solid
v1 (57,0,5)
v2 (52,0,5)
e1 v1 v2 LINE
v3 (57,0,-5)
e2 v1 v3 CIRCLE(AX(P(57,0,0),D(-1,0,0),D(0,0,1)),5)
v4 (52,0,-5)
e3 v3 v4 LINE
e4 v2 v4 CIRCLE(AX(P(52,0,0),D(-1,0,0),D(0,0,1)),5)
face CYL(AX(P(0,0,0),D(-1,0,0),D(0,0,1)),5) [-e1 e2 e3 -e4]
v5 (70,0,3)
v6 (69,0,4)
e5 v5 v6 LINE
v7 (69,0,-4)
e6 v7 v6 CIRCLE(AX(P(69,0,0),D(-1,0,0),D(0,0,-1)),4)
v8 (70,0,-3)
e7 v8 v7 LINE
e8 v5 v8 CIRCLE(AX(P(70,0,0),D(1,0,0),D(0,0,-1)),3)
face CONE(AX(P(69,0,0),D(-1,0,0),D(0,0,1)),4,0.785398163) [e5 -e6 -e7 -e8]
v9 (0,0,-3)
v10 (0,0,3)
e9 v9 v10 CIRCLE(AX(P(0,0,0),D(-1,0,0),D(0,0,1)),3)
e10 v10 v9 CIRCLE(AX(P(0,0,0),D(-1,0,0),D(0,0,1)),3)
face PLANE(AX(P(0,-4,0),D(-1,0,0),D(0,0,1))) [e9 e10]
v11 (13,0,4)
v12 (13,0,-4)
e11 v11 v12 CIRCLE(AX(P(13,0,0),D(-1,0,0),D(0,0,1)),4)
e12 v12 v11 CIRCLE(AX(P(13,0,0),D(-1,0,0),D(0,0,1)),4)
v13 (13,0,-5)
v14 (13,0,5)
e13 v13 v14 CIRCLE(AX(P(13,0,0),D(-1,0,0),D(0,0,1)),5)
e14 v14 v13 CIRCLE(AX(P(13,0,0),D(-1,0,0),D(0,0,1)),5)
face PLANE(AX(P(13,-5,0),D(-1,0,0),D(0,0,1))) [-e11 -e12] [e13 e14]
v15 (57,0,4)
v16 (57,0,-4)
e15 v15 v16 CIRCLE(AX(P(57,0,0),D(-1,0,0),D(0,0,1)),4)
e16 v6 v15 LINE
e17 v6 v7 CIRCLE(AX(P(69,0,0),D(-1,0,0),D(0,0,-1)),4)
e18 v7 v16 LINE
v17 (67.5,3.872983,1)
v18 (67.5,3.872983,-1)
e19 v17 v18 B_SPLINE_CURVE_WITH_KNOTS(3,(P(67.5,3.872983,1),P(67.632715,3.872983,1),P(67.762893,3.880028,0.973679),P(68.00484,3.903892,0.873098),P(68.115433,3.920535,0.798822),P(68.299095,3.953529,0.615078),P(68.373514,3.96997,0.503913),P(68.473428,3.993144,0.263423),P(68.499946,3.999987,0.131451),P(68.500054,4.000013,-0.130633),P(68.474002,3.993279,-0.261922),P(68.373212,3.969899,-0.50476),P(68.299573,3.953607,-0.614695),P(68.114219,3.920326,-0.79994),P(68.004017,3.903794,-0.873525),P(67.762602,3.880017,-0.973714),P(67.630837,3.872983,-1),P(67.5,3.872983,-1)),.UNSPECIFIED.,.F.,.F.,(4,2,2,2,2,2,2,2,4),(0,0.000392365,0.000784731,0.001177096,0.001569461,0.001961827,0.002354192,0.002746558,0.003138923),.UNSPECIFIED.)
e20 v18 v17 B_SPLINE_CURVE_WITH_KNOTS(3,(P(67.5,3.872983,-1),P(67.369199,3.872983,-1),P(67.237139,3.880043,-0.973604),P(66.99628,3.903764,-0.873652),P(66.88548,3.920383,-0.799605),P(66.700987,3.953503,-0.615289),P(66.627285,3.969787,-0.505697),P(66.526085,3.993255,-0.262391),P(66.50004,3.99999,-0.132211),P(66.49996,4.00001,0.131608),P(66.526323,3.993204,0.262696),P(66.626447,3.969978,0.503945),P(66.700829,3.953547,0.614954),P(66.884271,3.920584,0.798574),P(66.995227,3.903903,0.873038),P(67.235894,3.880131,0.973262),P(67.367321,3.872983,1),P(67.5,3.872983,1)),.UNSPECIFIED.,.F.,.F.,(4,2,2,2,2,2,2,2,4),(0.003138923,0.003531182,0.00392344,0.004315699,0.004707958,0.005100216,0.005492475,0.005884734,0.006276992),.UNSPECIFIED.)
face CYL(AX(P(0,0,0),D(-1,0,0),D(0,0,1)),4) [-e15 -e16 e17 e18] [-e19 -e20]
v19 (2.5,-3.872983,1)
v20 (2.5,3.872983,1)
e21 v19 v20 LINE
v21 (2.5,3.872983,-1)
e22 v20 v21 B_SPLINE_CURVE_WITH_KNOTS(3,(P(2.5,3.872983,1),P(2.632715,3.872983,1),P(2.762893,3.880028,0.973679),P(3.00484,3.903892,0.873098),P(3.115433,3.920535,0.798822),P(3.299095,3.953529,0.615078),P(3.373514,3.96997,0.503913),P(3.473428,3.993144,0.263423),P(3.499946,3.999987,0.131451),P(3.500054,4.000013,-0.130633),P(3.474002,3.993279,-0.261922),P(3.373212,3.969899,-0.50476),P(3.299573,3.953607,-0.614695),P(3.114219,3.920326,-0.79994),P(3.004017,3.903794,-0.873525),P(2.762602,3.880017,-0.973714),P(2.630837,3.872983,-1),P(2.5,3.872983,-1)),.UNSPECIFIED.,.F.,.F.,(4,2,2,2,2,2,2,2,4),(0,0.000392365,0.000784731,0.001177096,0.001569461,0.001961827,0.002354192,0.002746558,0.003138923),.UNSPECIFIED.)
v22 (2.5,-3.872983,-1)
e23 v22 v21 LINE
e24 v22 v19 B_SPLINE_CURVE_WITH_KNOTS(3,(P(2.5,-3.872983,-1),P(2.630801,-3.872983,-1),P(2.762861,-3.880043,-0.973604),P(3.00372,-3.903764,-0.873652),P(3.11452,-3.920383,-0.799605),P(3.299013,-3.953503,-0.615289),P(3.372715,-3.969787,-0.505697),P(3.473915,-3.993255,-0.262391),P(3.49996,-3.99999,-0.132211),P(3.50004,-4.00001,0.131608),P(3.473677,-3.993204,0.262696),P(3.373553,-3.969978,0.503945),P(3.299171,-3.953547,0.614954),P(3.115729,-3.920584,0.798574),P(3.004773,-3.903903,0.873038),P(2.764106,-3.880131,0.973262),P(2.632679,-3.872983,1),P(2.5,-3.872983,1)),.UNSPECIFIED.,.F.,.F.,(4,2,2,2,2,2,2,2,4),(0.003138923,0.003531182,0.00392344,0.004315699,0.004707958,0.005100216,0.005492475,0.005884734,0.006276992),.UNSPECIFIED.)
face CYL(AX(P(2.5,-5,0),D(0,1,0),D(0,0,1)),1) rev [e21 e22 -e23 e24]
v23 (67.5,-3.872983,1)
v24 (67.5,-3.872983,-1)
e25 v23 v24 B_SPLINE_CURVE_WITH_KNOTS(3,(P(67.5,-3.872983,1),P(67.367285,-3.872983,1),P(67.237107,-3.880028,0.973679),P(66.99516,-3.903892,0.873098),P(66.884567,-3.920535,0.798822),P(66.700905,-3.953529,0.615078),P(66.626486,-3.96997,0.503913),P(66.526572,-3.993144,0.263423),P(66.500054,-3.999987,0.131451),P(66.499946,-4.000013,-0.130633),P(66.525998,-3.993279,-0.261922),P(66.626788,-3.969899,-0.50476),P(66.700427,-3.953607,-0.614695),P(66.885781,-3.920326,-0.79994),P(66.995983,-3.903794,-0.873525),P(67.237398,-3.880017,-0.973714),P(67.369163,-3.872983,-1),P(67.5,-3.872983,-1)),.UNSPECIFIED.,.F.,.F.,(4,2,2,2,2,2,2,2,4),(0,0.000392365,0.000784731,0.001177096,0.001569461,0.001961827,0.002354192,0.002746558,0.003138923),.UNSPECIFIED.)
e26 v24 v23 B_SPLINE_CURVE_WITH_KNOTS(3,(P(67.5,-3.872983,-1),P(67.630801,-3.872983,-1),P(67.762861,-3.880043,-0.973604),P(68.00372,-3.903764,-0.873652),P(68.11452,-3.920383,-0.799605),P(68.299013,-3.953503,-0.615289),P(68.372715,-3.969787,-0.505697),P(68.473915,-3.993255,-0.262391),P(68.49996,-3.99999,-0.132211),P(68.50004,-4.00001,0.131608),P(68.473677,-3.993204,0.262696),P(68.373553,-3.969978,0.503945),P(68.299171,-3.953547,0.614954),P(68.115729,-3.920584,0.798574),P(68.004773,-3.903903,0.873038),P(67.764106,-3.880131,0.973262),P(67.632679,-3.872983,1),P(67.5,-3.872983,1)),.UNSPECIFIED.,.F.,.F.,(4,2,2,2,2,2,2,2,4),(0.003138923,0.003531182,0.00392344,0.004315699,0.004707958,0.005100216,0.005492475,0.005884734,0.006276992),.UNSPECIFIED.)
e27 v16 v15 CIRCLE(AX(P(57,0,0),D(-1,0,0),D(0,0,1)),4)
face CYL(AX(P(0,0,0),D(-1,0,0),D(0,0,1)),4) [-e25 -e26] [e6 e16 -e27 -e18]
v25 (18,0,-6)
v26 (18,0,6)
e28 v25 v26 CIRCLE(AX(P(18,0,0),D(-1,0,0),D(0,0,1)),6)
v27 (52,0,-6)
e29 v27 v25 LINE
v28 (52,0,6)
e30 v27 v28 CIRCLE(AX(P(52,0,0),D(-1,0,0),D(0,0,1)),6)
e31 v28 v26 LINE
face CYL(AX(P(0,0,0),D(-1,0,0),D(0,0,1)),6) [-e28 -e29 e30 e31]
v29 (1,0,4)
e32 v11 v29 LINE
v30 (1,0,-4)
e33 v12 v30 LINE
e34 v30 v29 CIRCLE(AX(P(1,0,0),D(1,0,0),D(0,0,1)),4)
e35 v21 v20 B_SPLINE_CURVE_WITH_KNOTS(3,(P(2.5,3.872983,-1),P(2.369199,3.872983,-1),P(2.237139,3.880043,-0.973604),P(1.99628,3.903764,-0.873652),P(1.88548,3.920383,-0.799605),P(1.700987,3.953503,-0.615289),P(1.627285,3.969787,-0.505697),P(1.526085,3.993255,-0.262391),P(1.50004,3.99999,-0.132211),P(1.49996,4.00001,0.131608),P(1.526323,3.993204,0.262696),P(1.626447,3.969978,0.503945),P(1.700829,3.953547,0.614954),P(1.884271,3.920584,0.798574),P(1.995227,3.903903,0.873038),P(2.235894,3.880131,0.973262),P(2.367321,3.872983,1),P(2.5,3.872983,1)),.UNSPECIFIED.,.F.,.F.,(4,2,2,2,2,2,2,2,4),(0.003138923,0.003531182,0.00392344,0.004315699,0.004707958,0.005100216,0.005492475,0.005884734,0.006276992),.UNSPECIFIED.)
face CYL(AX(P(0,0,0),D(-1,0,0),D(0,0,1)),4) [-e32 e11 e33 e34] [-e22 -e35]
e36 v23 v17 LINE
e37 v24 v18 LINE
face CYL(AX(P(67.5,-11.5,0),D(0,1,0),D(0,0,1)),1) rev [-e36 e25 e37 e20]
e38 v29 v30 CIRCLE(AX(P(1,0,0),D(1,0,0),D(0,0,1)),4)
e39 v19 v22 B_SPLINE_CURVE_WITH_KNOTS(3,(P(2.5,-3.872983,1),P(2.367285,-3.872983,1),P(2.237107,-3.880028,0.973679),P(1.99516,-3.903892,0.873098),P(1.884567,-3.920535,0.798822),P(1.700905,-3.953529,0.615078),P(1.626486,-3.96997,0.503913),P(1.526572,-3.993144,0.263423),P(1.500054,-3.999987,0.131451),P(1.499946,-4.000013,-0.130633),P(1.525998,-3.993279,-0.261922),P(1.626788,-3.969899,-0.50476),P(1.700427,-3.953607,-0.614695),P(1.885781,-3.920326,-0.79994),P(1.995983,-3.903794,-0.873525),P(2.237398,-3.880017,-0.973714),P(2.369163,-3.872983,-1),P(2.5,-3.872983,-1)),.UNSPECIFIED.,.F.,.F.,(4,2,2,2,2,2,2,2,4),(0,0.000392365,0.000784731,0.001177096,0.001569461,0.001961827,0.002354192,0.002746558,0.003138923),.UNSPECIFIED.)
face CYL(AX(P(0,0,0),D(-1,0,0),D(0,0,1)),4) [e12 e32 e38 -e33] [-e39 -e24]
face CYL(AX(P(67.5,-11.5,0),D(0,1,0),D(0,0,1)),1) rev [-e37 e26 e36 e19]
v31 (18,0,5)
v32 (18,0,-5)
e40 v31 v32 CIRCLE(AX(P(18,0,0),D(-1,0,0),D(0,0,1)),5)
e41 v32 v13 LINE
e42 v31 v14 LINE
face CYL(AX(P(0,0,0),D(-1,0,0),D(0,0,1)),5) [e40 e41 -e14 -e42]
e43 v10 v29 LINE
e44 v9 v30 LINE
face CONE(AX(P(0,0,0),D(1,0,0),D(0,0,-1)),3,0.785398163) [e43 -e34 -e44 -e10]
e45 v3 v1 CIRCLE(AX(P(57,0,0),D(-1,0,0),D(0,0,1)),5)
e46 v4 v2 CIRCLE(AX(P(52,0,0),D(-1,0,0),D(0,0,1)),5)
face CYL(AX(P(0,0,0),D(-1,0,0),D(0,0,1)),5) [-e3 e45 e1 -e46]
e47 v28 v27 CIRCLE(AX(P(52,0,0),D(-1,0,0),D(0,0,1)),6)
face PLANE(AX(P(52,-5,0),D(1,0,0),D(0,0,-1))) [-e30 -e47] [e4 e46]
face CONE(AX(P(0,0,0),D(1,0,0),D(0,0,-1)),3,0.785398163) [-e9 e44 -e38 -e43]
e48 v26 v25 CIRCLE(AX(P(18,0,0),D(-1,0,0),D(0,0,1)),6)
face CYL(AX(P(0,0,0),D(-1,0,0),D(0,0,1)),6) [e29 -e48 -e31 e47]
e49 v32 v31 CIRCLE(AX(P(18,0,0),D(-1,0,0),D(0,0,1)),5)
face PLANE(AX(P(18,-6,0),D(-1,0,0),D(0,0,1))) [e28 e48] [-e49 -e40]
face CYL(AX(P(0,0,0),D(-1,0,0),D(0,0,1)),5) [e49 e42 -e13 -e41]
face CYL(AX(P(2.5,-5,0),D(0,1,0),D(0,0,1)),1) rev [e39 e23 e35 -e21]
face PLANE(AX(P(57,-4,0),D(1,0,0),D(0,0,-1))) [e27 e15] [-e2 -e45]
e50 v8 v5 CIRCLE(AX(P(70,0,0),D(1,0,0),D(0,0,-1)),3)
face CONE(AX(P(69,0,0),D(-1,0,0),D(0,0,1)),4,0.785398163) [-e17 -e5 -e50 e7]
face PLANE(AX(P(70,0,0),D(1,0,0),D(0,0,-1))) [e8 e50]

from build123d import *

# Parameters (mm, degrees)
CROSS_HOLE_2_END_1_SKETCH_R = 1
CROSS_HOLE_2_END_1_DEPTH    = 5
CROSS_HOLE_2_END_2_SKETCH_R = 1
CROSS_HOLE_2_END_2_DEPTH    = 11.5
END_CHAMFER_1X45_SIZE       = 1


with BuildPart() as part:
    # Shaft Profile Sketch → Stepped Shaft Body (revolve)
    with BuildSketch(Plane.XY, mode=Mode.PRIVATE) as stepped_shaft_body_sk:
        Polygon((0, 0), (70, 0), (70, -4), (57, -4), (57, -5), (52, -5), (52, -6), (18, -6), (18, -5), (13, -5), (13, -4), (0, -4), align=None)
    revolve(stepped_shaft_body_sk.sketch.rotate(Axis((0, 0, 0), (1, 0, 0)), 270), axis=Axis((0, 0, 0), (1, 0, 0)))

    # Cross Hole Ø2 End 1 Sketch → Cross Hole Ø2 End 1 (cut, symmetric)
    with BuildSketch(Plane(origin=(0, 0, 0), x_dir=(1, 0, 0), z_dir=(0, 1, 0))):
        with Locations(Location((2.5, 0, 0), (0, 0, 270))):
            Circle(CROSS_HOLE_2_END_1_SKETCH_R)
    extrude(amount=CROSS_HOLE_2_END_1_DEPTH, both=True, mode=Mode.SUBTRACT)

    # Cross Hole Ø2 End 2 Sketch → Cross Hole Ø2 End 2 (cut, symmetric)
    with BuildSketch(Plane(origin=(0, 0, 0), x_dir=(1, 0, 0), z_dir=(0, 1, 0))):
        with Locations(Location((67.5, 0, 0), (0, 0, 270))):
            Circle(CROSS_HOLE_2_END_2_SKETCH_R)
    extrude(amount=CROSS_HOLE_2_END_2_DEPTH, both=True, mode=Mode.SUBTRACT)

    # End Chamfer 1x45°
    end_chamfer_1x45_edges = [part.edges().sort_by_distance(p)[0] for p in [
        (70, 0, -4),
        (0, 0, -4),
    ]]
    chamfer(end_chamfer_1x45_edges, length=END_CHAMFER_1X45_SIZE)


solid = part.part
